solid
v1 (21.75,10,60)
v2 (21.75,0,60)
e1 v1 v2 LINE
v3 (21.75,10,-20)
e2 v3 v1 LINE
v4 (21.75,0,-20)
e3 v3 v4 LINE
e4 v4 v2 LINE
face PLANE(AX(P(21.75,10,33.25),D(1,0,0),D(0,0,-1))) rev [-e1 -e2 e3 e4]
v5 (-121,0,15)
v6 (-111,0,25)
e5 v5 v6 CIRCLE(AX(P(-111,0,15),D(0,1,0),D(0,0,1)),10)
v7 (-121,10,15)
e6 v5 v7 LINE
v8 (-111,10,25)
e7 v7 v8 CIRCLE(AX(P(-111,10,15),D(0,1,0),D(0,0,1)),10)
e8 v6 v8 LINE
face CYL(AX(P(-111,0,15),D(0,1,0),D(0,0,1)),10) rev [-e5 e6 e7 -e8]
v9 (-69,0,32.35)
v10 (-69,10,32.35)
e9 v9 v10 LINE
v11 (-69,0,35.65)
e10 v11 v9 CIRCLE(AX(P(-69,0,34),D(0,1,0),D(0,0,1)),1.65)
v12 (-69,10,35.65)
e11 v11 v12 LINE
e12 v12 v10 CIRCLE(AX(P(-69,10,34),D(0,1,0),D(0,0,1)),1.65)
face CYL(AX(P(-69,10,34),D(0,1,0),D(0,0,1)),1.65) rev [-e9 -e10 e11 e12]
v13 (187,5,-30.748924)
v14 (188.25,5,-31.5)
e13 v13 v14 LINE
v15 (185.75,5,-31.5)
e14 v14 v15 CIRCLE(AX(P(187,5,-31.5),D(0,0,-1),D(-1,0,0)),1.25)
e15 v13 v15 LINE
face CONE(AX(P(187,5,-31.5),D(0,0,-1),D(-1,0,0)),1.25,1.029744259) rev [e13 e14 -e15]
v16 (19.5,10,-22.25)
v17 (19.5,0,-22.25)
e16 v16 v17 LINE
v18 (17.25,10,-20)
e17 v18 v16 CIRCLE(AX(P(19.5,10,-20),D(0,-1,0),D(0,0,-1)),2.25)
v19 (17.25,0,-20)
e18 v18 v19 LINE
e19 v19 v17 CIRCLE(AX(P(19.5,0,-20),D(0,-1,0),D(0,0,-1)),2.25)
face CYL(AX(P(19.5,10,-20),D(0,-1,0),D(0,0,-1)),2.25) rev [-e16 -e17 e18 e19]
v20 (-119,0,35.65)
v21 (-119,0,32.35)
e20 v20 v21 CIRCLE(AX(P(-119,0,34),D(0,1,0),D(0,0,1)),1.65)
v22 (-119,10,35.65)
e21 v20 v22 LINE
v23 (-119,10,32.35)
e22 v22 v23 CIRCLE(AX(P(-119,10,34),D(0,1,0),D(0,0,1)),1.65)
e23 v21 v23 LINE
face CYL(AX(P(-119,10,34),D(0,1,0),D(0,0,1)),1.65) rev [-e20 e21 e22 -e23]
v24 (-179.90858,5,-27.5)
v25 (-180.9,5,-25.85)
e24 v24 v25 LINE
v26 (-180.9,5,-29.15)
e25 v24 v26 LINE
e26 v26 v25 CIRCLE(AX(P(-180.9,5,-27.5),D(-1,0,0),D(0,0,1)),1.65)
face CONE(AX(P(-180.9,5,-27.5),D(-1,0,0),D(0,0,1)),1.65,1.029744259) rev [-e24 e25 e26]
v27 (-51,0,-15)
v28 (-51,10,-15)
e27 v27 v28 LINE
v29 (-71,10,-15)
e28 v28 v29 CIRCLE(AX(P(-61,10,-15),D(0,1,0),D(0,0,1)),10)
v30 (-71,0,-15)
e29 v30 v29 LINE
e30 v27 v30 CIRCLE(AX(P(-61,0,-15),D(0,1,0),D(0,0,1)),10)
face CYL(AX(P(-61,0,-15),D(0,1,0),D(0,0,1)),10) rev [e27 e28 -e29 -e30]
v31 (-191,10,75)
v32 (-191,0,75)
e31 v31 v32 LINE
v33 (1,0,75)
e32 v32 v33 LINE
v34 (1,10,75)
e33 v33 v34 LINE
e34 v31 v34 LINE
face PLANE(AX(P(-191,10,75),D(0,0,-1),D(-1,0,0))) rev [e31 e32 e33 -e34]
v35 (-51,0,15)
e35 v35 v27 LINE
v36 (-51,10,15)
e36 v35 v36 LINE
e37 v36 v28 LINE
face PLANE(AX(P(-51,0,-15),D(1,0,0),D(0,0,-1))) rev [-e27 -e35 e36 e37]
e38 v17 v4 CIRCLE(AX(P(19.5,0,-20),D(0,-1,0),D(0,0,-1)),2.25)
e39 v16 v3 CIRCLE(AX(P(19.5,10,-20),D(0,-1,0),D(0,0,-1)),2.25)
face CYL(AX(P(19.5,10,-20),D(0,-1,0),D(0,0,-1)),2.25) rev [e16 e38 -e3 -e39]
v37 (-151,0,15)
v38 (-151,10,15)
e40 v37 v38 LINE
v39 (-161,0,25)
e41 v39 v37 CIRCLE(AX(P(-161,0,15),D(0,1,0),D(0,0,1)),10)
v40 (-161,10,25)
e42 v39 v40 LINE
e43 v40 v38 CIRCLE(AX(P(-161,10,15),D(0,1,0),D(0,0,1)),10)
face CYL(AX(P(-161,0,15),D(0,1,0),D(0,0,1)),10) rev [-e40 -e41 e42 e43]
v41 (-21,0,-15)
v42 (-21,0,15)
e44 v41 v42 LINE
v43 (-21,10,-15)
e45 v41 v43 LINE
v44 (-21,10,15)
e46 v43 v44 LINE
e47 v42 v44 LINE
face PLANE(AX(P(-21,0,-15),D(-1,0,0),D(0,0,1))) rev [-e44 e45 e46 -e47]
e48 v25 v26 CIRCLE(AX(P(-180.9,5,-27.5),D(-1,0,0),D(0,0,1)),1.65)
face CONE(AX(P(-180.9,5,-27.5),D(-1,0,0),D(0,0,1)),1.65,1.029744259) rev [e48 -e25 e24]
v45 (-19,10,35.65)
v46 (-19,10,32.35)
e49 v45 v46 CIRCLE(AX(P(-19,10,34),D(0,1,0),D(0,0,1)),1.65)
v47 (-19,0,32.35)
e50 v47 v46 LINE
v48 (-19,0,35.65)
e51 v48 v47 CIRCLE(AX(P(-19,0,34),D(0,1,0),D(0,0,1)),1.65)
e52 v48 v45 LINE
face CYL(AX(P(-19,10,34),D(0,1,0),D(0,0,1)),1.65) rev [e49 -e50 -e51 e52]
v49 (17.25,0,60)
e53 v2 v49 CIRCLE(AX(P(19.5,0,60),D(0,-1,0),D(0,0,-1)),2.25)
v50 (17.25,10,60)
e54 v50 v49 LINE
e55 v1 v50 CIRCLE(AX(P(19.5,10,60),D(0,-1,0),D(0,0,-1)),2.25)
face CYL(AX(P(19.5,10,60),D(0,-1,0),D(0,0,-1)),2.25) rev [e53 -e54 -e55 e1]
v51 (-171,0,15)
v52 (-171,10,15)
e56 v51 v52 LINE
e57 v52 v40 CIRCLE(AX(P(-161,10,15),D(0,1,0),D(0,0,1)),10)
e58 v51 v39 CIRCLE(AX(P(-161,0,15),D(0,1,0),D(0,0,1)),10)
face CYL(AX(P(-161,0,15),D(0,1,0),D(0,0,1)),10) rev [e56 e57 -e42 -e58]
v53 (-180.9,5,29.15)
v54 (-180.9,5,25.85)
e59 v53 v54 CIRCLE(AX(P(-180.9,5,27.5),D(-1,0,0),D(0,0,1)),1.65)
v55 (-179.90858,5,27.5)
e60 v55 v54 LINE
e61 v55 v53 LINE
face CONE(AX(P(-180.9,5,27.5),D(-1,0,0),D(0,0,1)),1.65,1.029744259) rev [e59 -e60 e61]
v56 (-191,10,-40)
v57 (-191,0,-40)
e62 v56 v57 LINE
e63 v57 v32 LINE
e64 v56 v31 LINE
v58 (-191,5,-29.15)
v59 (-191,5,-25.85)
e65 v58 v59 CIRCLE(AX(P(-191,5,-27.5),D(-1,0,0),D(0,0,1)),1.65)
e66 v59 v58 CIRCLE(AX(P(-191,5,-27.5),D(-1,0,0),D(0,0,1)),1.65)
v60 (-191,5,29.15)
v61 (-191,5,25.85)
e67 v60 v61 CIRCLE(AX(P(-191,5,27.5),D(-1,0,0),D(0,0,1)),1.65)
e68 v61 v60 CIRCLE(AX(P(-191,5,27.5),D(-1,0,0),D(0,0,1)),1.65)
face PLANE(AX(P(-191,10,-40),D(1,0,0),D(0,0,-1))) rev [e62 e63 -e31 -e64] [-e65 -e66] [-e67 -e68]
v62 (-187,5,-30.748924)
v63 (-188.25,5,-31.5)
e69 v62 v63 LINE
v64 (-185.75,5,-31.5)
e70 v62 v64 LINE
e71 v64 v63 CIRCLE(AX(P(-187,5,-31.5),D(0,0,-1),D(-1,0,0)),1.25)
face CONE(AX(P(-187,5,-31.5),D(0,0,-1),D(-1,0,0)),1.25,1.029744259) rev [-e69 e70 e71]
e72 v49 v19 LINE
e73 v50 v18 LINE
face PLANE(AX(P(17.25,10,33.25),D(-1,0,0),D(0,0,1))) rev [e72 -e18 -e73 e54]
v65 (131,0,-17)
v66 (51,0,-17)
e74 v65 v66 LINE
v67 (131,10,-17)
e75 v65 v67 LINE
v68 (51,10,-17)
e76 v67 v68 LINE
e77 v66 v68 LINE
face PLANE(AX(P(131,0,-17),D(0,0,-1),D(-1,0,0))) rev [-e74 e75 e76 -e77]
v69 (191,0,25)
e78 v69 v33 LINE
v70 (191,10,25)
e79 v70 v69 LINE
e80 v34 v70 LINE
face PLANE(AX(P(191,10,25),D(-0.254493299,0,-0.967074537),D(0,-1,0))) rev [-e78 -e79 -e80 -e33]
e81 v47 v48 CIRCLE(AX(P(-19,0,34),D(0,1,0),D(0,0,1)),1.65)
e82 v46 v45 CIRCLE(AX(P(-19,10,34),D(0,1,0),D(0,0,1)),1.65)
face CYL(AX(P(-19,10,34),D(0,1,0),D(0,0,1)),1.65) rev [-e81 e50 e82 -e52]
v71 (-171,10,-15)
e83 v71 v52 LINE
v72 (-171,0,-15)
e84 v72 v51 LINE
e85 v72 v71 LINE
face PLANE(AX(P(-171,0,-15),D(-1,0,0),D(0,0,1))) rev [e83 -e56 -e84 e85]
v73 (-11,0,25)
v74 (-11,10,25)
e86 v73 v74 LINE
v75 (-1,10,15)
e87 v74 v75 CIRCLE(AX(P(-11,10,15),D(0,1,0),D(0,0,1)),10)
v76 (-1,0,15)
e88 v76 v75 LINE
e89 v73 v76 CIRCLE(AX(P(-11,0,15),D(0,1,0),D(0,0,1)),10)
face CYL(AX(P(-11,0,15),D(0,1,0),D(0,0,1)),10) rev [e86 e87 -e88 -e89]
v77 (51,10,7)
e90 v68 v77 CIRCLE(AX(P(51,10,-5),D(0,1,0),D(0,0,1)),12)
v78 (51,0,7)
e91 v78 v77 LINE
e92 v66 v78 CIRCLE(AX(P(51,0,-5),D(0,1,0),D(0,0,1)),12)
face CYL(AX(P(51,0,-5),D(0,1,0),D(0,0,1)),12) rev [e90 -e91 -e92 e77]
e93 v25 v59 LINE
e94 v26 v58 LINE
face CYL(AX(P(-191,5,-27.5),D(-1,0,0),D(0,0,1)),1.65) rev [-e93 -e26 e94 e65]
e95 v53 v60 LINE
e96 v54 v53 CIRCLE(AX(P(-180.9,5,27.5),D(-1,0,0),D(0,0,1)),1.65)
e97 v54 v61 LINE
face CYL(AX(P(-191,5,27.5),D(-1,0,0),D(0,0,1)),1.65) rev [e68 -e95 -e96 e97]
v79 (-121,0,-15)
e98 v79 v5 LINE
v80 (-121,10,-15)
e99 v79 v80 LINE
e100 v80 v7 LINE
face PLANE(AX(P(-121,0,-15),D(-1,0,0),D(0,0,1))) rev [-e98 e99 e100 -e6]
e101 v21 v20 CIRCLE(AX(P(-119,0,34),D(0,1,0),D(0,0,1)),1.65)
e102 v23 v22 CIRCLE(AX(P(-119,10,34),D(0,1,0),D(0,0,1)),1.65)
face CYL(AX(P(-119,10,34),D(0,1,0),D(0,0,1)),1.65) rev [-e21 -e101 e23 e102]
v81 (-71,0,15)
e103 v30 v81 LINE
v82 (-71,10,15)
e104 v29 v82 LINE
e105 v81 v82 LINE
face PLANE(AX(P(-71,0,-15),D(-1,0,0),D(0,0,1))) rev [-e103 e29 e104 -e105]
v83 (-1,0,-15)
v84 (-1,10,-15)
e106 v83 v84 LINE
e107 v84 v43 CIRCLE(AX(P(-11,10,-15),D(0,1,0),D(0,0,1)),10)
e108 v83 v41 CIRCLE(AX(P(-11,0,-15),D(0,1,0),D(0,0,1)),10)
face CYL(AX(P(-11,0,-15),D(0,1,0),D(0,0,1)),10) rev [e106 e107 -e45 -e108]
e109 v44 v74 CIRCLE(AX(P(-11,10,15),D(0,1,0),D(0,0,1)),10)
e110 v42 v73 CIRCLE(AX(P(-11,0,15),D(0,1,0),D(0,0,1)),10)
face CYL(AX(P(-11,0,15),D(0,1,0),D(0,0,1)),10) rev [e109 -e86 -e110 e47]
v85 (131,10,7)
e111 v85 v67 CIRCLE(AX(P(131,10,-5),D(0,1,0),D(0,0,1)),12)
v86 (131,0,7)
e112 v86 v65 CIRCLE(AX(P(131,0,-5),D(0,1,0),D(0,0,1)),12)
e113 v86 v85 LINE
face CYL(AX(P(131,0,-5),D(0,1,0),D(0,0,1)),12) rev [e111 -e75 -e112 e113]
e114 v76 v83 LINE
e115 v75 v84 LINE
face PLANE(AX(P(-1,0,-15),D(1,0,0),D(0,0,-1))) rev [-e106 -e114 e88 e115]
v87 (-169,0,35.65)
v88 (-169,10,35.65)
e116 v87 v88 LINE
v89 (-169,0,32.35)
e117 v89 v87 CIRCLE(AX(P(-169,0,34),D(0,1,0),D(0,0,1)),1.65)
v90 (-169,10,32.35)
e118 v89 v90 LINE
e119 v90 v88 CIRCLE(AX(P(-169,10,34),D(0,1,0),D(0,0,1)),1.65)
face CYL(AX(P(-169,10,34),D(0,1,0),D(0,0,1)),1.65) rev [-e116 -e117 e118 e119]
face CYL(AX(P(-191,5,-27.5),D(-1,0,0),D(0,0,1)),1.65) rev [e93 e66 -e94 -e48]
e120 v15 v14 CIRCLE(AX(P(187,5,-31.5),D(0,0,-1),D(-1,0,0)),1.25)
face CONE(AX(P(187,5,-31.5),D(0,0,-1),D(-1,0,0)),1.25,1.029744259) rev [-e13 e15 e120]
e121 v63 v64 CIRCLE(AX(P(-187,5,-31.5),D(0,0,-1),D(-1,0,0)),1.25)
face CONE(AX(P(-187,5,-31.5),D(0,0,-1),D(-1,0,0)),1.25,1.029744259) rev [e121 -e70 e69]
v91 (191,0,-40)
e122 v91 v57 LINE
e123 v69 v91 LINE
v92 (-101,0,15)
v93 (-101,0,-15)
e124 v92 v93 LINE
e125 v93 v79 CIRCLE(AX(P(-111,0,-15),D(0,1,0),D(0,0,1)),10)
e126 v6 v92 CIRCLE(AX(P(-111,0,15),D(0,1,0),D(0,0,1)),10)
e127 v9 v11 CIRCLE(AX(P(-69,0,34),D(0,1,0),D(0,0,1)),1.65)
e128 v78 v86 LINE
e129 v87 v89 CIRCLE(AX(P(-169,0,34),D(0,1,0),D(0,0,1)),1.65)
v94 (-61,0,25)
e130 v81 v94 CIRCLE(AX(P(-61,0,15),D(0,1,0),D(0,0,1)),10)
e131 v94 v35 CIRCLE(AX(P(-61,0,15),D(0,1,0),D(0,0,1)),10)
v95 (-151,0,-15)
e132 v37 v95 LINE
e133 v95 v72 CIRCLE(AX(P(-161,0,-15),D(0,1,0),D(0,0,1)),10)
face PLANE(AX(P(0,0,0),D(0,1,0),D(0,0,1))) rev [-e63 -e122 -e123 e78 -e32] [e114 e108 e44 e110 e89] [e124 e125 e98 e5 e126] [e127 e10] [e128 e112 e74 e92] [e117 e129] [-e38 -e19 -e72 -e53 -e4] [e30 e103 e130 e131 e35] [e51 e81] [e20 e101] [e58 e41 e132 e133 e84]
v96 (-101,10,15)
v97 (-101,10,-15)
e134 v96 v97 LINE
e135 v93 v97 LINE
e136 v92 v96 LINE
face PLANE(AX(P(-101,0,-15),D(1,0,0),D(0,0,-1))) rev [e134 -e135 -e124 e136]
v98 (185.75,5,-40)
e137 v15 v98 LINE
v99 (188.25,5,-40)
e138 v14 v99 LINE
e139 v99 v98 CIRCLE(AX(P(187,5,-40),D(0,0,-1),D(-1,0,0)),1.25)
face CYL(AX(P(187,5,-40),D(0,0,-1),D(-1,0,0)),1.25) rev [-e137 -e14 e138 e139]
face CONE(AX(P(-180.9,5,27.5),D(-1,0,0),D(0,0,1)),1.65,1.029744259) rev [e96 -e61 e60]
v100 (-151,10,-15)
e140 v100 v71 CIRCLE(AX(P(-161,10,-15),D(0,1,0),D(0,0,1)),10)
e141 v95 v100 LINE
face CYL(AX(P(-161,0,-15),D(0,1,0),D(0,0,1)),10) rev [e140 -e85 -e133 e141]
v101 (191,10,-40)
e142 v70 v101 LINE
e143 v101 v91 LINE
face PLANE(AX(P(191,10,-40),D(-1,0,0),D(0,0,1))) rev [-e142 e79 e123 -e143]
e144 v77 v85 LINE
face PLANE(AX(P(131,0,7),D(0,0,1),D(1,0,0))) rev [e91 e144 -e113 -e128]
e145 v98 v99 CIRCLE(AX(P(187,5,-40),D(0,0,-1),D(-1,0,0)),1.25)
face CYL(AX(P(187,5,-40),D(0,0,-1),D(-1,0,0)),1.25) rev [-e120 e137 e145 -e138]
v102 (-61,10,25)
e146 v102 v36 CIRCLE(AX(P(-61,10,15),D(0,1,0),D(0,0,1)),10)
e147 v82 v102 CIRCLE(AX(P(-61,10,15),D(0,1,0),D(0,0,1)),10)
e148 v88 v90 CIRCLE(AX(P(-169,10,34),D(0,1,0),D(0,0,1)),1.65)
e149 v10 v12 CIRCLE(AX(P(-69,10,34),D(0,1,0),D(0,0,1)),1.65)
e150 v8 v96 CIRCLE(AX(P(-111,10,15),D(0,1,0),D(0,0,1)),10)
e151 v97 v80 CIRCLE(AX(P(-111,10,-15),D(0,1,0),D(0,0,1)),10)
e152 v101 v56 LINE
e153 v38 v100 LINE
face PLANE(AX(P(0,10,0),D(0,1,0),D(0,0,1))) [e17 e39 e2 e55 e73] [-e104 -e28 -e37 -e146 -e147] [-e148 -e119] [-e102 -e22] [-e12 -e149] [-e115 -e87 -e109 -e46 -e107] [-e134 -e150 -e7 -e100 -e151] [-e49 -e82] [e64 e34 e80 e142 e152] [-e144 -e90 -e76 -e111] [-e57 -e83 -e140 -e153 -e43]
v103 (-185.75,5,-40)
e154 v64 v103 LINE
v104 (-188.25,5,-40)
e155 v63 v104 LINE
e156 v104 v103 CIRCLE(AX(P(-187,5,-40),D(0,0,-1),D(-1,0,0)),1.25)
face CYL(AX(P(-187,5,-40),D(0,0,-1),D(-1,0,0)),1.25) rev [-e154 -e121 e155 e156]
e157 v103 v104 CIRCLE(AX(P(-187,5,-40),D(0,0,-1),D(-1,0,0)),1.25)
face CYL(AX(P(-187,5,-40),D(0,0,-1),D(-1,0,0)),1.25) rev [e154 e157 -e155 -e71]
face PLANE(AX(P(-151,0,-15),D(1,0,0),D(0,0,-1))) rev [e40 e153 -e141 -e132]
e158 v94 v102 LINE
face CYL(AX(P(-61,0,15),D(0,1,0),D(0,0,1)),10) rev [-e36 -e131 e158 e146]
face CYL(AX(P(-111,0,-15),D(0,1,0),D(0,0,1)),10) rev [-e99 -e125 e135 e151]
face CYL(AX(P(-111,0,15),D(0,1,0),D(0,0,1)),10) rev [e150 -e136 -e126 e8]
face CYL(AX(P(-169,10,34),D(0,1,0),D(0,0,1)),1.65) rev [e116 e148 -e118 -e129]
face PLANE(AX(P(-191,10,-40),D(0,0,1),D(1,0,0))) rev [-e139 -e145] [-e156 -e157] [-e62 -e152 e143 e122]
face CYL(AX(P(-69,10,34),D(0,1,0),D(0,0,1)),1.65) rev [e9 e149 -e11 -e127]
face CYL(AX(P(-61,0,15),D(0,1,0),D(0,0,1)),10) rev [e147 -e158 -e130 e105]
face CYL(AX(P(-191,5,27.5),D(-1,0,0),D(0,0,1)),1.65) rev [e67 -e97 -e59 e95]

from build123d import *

# Parameters (mm, degrees)
SKETCH_1_W             = 382
SKETCH_1_H             = 80
EXTRUDE_1_DEPTH        = 10
HOLE_WIZARD_M3_1_D     = 2.5
HOLE_WIZARD_M3_1_DEPTH = 8.5
HOLE_WIZARD_M3_1_TIP   = 0.751075774
CUT_EXTRUDE_1_DEPTH    = 196.399590583
PATTERN_LINEAR_1_COUNT = 4
PATTERN_LINEAR_1_PITCH = 50
HOLE_WIZARD_M4_1_D     = 4.5
HOLE_WIZARD_M4_1_2_D   = 3.3
PATTERN_LINEAR_2_COUNT = 4
PATTERN_LINEAR_2_PITCH = 50
HOLE_WIZARD_M4_2_D     = 3.3
HOLE_WIZARD_M4_2_DEPTH = 10.1
HOLE_WIZARD_M4_2_TIP   = 0.991420021
CUT_EXTRUDE_3_DEPTH    = 10
MOVE_FACE_1_BY         = 35
CUT_EXTRUDE_4_DEPTH    = 206.440989094
CHAMFER_1_SIZE         = 190
CHAMFER_1_SIZE2        = 50
CUT_EXTRUDE_2_DEPTH    = 206.440989094


with BuildPart() as part:
    # 草图1 → 凸台-拉伸1 (new body)
    with BuildSketch(Plane(origin=(0, 0, 0), x_dir=(1, 0, 0), z_dir=(0, 1, 0))):
        Rectangle(SKETCH_1_W, SKETCH_1_H)
    extrude(amount=EXTRUDE_1_DEPTH)

    # M3 螺纹孔1
    with Locations(Plane(origin=(0, 0, -40), x_dir=(-1, 0, 0), z_dir=(0, 0, -1))):
        with Locations((187, 5), (-187, 5)):
            Hole(HOLE_WIZARD_M3_1_D / 2, depth=HOLE_WIZARD_M3_1_DEPTH)
            with Locations((0, 0, -(HOLE_WIZARD_M3_1_DEPTH + HOLE_WIZARD_M3_1_TIP / 2))):  # 118° drill point
                Cone(0, HOLE_WIZARD_M3_1_D / 2, HOLE_WIZARD_M3_1_TIP, mode=Mode.SUBTRACT)

    # 草图4 → 切除-拉伸1 (cut, through all)
    with BuildSketch(Plane(origin=(0, 10, 0), x_dir=(1, 0, 0), z_dir=(0, 1, 0))):
        with BuildLine():
            Line((-1, 15), (-1, -15))
            ThreePointArc((-1, -15), (-11, -25), (-21, -15))
            Line((-21, -15), (-21, 15))
            ThreePointArc((-21, 15), (-11, 25), (-1, 15))
        make_face()
    cut_extrude_1 = extrude(amount=-CUT_EXTRUDE_1_DEPTH, mode=Mode.SUBTRACT)

    # 阵列(线性)1: 切除-拉伸1 ×4
    with Locations(*[(-i * PATTERN_LINEAR_1_PITCH, 0, 0) for i in range(1, PATTERN_LINEAR_1_COUNT)]):
        add(cut_extrude_1, mode=Mode.SUBTRACT)

    # Hole Wizard M4 _1 (through all)
    with Locations(Plane(origin=(0, 10, 0), x_dir=(1, 0, 0), z_dir=(0, 1, 0))):
        with Locations((19.5, -11), (19.5, -31)):
            Hole(HOLE_WIZARD_M4_1_D / 2)

    # Hole Wizard M4 _1 2 (through all)
    with Locations(Plane(origin=(0, 10, 0), x_dir=(1, 0, 0), z_dir=(0, 1, 0))):
        with Locations((-19, -34)):
            hole_wizard_m4_1_2 = Hole(HOLE_WIZARD_M4_1_2_D / 2)

    # 阵列(线性)2: Hole Wizard M4 _1 2 ×4
    with Locations(*[(-i * PATTERN_LINEAR_2_PITCH, 0, 0) for i in range(1, PATTERN_LINEAR_2_COUNT)]):
        add(hole_wizard_m4_1_2, mode=Mode.SUBTRACT)

    # M4 螺纹孔2
    with Locations(Plane.ZY.offset(191)):
        with Locations((27.5, 5), (-27.5, 5)):
            Hole(HOLE_WIZARD_M4_2_D / 2, depth=HOLE_WIZARD_M4_2_DEPTH)
            with Locations((0, 0, -(HOLE_WIZARD_M4_2_DEPTH + HOLE_WIZARD_M4_2_TIP / 2))):  # 118° drill point
                Cone(0, HOLE_WIZARD_M4_2_D / 2, HOLE_WIZARD_M4_2_TIP, mode=Mode.SUBTRACT)

    # 草图14 → 切除-拉伸3 (cut)
    with BuildSketch(Plane.XZ):
        with BuildLine():
            Line((21.749999636, 33.25), (21.749999636, 28.75))
            ThreePointArc((21.749999636, 28.75), (19.499999636, 26.5), (17.249999636, 28.75))
            Line((17.249999636, 28.75), (17.249999636, 33.25))
            ThreePointArc((17.249999636, 33.25), (19.499999636, 35.5), (21.749999636, 33.25))
        make_face()
        with BuildLine():
            Line((21.749999636, 13.25), (21.749999636, 8.75))
            ThreePointArc((21.749999636, 8.75), (19.499999636, 6.5), (17.249999636, 8.75))
            Line((17.249999636, 8.75), (17.249999636, 13.25))
            ThreePointArc((17.249999636, 13.25), (19.499999636, 15.5), (21.749999636, 13.25))
        make_face()
    extrude(amount=-CUT_EXTRUDE_3_DEPTH, mode=Mode.SUBTRACT)

    # Move Face 1: a face moved outward by 35.0
    extrude(part.faces().sort_by_distance((0, 5, 40))[0], amount=MOVE_FACE_1_BY, dir=(0, 0, 1))

    # 草图15 → 切除-拉伸4 (cut, through all)
    with BuildSketch(Plane.XZ):
        with BuildLine():
            Line((21.749999636, 60), (21.749999636, -20))
            ThreePointArc((21.749999636, -20), (19.499999636, -22.25), (17.249999636, -20))
            Line((17.249999636, -20), (17.249999636, 60))
            ThreePointArc((17.249999636, 60), (19.499999636, 62.25), (21.749999636, 60))
        make_face()
    extrude(amount=-CUT_EXTRUDE_4_DEPTH, mode=Mode.SUBTRACT)

    # 倒角1
    chamfer_1_edges = [part.edges().sort_by_distance(p)[0] for p in [
        (191, 5, 75),
    ]]
    chamfer_1_side = [part.faces().sort_by_distance(p)[0] for p in [
        (0, 5, 75),
    ]]
    chamfer(chamfer_1_edges, length=CHAMFER_1_SIZE, length2=CHAMFER_1_SIZE2, reference=chamfer_1_side[0])

    # 草图5 → 切除-拉伸2 (cut, through all)
    with BuildSketch(Plane(origin=(0, 10, 0), x_dir=(1, 0, 0), z_dir=(0, 1, 0))):
        with BuildLine():
            Line((131, -7), (51, -7))
            ThreePointArc((51, -7), (39, 5), (51, 17))
            Line((51, 17), (131, 17))
            ThreePointArc((131, 17), (143, 5), (131, -7))
        make_face()
    extrude(amount=-CUT_EXTRUDE_2_DEPTH, mode=Mode.SUBTRACT)


solid = part.part
